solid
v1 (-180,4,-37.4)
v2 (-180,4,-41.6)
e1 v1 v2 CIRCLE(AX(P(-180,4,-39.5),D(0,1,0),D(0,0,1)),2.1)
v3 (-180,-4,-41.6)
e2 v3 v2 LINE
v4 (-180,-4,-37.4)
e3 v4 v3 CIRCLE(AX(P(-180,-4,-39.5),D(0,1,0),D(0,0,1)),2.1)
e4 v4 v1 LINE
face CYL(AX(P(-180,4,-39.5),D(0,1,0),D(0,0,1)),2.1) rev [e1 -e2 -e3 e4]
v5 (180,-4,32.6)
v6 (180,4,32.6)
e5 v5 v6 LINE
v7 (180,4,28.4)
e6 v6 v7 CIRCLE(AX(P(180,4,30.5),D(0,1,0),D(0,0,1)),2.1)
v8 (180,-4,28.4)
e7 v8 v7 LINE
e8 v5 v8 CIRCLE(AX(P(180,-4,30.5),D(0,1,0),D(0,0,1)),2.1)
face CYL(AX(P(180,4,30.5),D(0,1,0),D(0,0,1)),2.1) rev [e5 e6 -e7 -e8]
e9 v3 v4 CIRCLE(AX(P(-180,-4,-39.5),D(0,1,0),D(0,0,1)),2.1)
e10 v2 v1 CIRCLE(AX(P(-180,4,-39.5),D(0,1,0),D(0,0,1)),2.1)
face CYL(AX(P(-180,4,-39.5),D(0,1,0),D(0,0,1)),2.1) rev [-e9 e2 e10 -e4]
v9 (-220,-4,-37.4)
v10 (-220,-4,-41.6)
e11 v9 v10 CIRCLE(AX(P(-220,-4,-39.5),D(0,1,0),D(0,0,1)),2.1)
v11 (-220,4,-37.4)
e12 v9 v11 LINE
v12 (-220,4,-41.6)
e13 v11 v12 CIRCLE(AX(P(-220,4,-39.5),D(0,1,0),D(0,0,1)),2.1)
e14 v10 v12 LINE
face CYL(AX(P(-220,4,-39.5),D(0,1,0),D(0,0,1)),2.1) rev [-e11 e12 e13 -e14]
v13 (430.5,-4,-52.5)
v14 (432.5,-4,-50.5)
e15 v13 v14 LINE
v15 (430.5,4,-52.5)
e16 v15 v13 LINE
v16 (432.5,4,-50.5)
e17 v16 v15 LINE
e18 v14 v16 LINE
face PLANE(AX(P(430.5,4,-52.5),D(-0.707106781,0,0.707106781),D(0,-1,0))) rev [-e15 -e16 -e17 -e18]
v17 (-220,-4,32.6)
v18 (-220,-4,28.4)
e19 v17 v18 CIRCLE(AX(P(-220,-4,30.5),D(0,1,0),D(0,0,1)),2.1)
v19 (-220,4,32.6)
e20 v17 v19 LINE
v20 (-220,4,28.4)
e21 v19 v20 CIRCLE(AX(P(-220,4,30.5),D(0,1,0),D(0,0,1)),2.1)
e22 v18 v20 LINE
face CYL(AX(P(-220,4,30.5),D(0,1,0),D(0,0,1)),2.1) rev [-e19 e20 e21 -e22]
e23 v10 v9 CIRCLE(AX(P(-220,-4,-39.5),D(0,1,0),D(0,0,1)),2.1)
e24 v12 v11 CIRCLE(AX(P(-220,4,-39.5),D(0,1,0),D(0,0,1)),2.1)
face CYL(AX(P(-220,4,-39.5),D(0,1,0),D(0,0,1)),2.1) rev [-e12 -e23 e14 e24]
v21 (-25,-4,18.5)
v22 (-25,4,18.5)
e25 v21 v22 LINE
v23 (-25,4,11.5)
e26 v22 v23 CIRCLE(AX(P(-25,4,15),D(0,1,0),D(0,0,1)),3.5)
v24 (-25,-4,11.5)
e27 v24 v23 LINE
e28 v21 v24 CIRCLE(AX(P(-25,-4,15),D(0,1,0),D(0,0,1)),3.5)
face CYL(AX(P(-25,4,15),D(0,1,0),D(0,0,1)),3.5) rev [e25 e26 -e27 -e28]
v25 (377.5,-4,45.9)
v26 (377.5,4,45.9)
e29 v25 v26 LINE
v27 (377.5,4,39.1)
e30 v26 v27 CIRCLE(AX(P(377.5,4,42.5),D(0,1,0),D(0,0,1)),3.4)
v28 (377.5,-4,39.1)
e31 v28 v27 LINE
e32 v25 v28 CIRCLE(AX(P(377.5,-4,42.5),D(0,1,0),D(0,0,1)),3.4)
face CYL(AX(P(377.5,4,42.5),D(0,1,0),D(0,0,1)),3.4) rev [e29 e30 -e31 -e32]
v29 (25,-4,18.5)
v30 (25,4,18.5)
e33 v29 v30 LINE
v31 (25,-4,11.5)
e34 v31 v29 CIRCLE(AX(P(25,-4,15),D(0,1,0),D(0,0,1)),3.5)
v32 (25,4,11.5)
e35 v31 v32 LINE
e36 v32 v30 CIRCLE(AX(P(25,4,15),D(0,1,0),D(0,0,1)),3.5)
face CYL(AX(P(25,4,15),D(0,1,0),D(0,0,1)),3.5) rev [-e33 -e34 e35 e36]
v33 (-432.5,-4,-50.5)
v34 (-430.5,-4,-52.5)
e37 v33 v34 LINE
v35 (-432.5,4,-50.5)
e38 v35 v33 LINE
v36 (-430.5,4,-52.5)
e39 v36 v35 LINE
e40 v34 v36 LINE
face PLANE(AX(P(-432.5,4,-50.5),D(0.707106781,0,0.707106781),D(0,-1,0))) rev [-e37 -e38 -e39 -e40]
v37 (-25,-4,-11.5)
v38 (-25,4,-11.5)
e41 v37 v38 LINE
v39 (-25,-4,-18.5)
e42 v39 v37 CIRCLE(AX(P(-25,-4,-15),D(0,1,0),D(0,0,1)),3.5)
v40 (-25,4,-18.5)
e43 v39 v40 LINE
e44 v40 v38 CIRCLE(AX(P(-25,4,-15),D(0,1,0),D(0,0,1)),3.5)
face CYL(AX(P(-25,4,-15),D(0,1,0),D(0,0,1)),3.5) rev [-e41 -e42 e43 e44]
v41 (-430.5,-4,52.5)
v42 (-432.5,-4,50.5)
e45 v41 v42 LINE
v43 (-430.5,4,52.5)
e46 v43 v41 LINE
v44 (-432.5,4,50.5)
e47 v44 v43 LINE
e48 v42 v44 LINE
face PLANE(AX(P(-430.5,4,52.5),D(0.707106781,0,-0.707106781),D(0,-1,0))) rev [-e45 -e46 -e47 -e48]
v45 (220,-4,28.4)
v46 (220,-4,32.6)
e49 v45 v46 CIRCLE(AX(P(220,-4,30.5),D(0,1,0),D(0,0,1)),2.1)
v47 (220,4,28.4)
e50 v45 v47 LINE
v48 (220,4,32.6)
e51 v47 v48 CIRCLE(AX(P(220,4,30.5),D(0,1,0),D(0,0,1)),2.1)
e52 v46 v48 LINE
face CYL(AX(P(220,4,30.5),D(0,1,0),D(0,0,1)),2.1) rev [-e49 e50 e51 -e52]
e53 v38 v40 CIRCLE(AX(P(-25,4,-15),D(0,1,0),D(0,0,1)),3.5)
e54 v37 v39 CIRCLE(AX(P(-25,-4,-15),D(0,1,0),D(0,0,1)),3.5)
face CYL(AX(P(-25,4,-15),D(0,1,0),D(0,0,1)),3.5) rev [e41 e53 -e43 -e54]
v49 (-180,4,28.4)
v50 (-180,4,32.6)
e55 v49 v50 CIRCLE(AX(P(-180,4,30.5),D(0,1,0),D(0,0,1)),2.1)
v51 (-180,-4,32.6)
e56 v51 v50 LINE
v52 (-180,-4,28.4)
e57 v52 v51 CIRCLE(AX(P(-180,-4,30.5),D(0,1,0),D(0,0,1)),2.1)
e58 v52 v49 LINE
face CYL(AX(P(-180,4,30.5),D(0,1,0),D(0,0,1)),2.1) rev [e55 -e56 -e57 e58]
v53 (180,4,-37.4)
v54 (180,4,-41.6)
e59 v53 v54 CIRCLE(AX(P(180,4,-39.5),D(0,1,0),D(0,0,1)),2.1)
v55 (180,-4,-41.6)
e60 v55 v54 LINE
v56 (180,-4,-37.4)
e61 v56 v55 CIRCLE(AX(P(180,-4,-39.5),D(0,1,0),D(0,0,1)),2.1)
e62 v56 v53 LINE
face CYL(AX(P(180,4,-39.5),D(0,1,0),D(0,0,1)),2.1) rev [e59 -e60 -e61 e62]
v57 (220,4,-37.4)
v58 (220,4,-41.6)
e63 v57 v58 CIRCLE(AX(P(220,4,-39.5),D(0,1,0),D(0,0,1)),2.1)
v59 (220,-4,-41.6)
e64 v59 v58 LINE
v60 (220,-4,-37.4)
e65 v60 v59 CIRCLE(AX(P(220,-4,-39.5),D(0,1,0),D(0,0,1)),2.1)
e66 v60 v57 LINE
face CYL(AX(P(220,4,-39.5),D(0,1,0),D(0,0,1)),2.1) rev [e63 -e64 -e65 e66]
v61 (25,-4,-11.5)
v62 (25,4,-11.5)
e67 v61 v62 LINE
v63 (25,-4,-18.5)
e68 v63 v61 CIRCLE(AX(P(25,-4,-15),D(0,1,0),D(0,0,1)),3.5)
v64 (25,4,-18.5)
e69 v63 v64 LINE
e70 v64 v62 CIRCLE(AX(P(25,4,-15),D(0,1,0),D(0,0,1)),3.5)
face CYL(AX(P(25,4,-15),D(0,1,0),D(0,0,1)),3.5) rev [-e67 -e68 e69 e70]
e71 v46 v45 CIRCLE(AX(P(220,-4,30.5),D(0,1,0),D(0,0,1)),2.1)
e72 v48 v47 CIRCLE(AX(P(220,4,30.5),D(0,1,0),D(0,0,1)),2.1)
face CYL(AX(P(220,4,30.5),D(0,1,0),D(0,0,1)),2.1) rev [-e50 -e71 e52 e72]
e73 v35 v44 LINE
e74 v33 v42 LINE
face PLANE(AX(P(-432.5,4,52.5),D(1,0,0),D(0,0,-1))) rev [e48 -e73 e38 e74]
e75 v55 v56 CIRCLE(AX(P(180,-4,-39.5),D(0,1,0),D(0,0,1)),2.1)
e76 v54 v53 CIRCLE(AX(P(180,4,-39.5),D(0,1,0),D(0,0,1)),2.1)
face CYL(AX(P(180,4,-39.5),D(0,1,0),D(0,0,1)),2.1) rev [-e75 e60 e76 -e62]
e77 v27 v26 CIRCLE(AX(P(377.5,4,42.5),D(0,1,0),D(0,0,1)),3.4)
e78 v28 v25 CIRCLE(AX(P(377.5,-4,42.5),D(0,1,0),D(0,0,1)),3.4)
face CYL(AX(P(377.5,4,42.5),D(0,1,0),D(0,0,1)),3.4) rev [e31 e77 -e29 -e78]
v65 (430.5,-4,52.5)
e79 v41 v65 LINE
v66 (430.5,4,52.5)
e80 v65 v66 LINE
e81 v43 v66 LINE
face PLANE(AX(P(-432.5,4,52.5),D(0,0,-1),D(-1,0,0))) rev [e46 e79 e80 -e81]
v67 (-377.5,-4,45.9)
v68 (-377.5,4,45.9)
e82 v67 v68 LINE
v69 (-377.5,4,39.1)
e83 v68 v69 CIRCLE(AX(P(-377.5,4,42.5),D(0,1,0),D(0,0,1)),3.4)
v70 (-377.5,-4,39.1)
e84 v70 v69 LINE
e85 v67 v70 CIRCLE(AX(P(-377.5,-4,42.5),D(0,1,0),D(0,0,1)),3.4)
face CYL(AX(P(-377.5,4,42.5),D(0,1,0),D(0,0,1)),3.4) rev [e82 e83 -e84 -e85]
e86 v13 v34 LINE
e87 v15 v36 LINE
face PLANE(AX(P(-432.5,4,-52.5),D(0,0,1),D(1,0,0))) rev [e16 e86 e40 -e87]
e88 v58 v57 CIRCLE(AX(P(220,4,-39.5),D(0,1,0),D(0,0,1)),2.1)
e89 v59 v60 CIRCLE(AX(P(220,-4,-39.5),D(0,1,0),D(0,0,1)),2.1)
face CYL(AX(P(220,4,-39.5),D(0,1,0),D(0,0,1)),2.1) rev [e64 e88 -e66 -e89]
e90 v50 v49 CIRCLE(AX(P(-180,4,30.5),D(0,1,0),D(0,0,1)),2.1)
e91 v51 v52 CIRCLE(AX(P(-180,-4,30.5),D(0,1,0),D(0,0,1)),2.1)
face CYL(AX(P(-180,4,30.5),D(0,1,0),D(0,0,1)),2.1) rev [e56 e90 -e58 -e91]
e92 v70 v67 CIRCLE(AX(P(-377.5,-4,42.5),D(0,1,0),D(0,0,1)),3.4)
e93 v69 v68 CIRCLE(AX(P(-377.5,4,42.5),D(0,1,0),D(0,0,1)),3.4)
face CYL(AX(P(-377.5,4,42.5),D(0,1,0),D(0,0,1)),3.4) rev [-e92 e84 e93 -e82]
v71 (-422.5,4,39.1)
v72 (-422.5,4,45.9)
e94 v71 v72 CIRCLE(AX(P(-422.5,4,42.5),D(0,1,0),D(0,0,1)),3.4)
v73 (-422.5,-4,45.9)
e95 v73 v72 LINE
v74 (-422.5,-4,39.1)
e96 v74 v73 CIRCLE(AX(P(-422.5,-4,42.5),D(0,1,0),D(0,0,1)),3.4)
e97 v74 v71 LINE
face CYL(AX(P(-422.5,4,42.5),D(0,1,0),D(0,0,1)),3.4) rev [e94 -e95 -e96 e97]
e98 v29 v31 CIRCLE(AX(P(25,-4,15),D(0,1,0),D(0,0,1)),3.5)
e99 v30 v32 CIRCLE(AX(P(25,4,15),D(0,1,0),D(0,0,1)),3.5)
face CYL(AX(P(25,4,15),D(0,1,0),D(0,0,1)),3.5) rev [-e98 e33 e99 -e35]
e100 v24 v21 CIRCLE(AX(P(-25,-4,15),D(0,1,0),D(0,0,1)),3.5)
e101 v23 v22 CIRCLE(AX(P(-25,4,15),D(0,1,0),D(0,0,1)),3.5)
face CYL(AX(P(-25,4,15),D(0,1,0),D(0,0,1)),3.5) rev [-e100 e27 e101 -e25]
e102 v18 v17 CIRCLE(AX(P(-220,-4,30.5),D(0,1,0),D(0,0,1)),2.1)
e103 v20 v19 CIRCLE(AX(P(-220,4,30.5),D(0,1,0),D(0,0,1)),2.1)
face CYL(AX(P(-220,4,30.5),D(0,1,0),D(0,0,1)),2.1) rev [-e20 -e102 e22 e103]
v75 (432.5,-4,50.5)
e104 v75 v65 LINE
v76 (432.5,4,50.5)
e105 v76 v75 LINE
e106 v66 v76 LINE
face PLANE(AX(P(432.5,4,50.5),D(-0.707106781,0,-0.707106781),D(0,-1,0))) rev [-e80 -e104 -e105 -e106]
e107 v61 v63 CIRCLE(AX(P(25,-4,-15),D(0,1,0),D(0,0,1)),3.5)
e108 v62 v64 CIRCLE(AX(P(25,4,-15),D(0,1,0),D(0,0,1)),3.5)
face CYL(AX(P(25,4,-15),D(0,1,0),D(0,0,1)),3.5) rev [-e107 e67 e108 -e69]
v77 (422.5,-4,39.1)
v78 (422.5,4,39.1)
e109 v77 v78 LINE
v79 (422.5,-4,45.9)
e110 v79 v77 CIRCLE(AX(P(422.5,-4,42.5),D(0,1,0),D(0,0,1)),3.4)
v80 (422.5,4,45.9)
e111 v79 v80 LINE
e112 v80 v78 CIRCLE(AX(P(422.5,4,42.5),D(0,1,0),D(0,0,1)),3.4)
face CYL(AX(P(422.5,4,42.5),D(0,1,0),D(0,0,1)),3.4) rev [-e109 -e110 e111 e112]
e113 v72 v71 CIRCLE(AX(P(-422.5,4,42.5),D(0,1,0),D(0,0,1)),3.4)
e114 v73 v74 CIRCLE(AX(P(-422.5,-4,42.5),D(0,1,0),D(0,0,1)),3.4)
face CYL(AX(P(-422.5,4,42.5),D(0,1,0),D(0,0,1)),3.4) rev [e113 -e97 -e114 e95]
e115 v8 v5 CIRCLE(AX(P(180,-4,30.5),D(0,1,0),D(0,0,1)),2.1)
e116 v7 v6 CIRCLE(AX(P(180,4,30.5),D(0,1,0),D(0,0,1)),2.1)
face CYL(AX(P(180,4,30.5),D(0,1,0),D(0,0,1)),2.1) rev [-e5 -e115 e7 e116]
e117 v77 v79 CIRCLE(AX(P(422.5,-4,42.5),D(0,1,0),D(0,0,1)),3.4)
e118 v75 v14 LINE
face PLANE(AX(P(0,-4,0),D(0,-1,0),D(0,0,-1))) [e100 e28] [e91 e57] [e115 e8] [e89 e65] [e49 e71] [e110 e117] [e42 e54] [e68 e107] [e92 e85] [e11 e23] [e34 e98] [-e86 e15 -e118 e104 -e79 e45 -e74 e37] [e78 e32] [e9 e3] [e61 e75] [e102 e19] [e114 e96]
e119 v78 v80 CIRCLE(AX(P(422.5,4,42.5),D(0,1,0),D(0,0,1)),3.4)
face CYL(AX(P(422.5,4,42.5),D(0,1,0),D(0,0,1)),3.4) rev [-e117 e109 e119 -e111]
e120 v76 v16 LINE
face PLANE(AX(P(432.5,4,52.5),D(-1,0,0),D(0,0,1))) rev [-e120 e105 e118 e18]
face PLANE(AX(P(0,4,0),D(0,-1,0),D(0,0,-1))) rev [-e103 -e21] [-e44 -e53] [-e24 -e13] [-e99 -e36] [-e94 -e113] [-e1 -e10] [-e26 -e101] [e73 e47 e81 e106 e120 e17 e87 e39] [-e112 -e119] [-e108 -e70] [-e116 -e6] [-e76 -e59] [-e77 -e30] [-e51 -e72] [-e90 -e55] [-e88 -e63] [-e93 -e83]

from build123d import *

# Parameters (mm, degrees)
SKETCH_1_W            = 865
SKETCH_1_H            = 105
EXTRUDE_1_DEPTH       = 4
CHAMFER_1_SIZE        = 2
HOLE_WIZARD_M5_1_D    = 4.2
HOLE_WIZARD_7_0_7_1_D = 7
HOLE_WIZARD_M8_1_D    = 6.8


with BuildPart() as part:
    # 草图1 → 凸台-拉伸1 (new, symmetric)
    with BuildSketch(Plane(origin=(0, 0, 0), x_dir=(1, 0, 0), z_dir=(0, 1, 0))):
        Rectangle(SKETCH_1_W, SKETCH_1_H)
    extrude(amount=EXTRUDE_1_DEPTH, both=True)

    # 倒角1
    chamfer_1_edges = [part.edges().sort_by_distance(p)[0] for p in [
        (432.5, 0, 52.5),
        (-432.5, 0, 52.5),
        (-432.5, 0, -52.5),
        (432.5, 0, -52.5),
    ]]
    chamfer(chamfer_1_edges, length=CHAMFER_1_SIZE)

    # M5 螺纹孔1 (through all)
    with Locations(Plane(origin=(0, 4, 0), x_dir=(1, 0, 0), z_dir=(0, 1, 0))):
        with Locations((-220, 39.5), (-180, 39.5), (-180, -30.5), (-220, -30.5), (220, -30.5), (180, -30.5), (180, 39.5), (220, 39.5)):
            Hole(HOLE_WIZARD_M5_1_D / 2)

    # Ø7.0 (7) 直径孔1 (through all)
    with Locations(Plane(origin=(0, 4, 0), x_dir=(1, 0, 0), z_dir=(0, 1, 0))):
        with Locations((25, -15), (25, 15), (-25, 15), (-25, -15)):
            Hole(HOLE_WIZARD_7_0_7_1_D / 2)

    # M8 螺纹孔1 (through all)
    with Locations(Plane(origin=(0, 4, 0), x_dir=(1, 0, 0), z_dir=(0, 1, 0))):
        with Locations((422.5, -42.5), (377.5, -42.5), (-377.5, -42.5), (-422.5, -42.5)):
            Hole(HOLE_WIZARD_M8_1_D / 2)


solid = part.part
